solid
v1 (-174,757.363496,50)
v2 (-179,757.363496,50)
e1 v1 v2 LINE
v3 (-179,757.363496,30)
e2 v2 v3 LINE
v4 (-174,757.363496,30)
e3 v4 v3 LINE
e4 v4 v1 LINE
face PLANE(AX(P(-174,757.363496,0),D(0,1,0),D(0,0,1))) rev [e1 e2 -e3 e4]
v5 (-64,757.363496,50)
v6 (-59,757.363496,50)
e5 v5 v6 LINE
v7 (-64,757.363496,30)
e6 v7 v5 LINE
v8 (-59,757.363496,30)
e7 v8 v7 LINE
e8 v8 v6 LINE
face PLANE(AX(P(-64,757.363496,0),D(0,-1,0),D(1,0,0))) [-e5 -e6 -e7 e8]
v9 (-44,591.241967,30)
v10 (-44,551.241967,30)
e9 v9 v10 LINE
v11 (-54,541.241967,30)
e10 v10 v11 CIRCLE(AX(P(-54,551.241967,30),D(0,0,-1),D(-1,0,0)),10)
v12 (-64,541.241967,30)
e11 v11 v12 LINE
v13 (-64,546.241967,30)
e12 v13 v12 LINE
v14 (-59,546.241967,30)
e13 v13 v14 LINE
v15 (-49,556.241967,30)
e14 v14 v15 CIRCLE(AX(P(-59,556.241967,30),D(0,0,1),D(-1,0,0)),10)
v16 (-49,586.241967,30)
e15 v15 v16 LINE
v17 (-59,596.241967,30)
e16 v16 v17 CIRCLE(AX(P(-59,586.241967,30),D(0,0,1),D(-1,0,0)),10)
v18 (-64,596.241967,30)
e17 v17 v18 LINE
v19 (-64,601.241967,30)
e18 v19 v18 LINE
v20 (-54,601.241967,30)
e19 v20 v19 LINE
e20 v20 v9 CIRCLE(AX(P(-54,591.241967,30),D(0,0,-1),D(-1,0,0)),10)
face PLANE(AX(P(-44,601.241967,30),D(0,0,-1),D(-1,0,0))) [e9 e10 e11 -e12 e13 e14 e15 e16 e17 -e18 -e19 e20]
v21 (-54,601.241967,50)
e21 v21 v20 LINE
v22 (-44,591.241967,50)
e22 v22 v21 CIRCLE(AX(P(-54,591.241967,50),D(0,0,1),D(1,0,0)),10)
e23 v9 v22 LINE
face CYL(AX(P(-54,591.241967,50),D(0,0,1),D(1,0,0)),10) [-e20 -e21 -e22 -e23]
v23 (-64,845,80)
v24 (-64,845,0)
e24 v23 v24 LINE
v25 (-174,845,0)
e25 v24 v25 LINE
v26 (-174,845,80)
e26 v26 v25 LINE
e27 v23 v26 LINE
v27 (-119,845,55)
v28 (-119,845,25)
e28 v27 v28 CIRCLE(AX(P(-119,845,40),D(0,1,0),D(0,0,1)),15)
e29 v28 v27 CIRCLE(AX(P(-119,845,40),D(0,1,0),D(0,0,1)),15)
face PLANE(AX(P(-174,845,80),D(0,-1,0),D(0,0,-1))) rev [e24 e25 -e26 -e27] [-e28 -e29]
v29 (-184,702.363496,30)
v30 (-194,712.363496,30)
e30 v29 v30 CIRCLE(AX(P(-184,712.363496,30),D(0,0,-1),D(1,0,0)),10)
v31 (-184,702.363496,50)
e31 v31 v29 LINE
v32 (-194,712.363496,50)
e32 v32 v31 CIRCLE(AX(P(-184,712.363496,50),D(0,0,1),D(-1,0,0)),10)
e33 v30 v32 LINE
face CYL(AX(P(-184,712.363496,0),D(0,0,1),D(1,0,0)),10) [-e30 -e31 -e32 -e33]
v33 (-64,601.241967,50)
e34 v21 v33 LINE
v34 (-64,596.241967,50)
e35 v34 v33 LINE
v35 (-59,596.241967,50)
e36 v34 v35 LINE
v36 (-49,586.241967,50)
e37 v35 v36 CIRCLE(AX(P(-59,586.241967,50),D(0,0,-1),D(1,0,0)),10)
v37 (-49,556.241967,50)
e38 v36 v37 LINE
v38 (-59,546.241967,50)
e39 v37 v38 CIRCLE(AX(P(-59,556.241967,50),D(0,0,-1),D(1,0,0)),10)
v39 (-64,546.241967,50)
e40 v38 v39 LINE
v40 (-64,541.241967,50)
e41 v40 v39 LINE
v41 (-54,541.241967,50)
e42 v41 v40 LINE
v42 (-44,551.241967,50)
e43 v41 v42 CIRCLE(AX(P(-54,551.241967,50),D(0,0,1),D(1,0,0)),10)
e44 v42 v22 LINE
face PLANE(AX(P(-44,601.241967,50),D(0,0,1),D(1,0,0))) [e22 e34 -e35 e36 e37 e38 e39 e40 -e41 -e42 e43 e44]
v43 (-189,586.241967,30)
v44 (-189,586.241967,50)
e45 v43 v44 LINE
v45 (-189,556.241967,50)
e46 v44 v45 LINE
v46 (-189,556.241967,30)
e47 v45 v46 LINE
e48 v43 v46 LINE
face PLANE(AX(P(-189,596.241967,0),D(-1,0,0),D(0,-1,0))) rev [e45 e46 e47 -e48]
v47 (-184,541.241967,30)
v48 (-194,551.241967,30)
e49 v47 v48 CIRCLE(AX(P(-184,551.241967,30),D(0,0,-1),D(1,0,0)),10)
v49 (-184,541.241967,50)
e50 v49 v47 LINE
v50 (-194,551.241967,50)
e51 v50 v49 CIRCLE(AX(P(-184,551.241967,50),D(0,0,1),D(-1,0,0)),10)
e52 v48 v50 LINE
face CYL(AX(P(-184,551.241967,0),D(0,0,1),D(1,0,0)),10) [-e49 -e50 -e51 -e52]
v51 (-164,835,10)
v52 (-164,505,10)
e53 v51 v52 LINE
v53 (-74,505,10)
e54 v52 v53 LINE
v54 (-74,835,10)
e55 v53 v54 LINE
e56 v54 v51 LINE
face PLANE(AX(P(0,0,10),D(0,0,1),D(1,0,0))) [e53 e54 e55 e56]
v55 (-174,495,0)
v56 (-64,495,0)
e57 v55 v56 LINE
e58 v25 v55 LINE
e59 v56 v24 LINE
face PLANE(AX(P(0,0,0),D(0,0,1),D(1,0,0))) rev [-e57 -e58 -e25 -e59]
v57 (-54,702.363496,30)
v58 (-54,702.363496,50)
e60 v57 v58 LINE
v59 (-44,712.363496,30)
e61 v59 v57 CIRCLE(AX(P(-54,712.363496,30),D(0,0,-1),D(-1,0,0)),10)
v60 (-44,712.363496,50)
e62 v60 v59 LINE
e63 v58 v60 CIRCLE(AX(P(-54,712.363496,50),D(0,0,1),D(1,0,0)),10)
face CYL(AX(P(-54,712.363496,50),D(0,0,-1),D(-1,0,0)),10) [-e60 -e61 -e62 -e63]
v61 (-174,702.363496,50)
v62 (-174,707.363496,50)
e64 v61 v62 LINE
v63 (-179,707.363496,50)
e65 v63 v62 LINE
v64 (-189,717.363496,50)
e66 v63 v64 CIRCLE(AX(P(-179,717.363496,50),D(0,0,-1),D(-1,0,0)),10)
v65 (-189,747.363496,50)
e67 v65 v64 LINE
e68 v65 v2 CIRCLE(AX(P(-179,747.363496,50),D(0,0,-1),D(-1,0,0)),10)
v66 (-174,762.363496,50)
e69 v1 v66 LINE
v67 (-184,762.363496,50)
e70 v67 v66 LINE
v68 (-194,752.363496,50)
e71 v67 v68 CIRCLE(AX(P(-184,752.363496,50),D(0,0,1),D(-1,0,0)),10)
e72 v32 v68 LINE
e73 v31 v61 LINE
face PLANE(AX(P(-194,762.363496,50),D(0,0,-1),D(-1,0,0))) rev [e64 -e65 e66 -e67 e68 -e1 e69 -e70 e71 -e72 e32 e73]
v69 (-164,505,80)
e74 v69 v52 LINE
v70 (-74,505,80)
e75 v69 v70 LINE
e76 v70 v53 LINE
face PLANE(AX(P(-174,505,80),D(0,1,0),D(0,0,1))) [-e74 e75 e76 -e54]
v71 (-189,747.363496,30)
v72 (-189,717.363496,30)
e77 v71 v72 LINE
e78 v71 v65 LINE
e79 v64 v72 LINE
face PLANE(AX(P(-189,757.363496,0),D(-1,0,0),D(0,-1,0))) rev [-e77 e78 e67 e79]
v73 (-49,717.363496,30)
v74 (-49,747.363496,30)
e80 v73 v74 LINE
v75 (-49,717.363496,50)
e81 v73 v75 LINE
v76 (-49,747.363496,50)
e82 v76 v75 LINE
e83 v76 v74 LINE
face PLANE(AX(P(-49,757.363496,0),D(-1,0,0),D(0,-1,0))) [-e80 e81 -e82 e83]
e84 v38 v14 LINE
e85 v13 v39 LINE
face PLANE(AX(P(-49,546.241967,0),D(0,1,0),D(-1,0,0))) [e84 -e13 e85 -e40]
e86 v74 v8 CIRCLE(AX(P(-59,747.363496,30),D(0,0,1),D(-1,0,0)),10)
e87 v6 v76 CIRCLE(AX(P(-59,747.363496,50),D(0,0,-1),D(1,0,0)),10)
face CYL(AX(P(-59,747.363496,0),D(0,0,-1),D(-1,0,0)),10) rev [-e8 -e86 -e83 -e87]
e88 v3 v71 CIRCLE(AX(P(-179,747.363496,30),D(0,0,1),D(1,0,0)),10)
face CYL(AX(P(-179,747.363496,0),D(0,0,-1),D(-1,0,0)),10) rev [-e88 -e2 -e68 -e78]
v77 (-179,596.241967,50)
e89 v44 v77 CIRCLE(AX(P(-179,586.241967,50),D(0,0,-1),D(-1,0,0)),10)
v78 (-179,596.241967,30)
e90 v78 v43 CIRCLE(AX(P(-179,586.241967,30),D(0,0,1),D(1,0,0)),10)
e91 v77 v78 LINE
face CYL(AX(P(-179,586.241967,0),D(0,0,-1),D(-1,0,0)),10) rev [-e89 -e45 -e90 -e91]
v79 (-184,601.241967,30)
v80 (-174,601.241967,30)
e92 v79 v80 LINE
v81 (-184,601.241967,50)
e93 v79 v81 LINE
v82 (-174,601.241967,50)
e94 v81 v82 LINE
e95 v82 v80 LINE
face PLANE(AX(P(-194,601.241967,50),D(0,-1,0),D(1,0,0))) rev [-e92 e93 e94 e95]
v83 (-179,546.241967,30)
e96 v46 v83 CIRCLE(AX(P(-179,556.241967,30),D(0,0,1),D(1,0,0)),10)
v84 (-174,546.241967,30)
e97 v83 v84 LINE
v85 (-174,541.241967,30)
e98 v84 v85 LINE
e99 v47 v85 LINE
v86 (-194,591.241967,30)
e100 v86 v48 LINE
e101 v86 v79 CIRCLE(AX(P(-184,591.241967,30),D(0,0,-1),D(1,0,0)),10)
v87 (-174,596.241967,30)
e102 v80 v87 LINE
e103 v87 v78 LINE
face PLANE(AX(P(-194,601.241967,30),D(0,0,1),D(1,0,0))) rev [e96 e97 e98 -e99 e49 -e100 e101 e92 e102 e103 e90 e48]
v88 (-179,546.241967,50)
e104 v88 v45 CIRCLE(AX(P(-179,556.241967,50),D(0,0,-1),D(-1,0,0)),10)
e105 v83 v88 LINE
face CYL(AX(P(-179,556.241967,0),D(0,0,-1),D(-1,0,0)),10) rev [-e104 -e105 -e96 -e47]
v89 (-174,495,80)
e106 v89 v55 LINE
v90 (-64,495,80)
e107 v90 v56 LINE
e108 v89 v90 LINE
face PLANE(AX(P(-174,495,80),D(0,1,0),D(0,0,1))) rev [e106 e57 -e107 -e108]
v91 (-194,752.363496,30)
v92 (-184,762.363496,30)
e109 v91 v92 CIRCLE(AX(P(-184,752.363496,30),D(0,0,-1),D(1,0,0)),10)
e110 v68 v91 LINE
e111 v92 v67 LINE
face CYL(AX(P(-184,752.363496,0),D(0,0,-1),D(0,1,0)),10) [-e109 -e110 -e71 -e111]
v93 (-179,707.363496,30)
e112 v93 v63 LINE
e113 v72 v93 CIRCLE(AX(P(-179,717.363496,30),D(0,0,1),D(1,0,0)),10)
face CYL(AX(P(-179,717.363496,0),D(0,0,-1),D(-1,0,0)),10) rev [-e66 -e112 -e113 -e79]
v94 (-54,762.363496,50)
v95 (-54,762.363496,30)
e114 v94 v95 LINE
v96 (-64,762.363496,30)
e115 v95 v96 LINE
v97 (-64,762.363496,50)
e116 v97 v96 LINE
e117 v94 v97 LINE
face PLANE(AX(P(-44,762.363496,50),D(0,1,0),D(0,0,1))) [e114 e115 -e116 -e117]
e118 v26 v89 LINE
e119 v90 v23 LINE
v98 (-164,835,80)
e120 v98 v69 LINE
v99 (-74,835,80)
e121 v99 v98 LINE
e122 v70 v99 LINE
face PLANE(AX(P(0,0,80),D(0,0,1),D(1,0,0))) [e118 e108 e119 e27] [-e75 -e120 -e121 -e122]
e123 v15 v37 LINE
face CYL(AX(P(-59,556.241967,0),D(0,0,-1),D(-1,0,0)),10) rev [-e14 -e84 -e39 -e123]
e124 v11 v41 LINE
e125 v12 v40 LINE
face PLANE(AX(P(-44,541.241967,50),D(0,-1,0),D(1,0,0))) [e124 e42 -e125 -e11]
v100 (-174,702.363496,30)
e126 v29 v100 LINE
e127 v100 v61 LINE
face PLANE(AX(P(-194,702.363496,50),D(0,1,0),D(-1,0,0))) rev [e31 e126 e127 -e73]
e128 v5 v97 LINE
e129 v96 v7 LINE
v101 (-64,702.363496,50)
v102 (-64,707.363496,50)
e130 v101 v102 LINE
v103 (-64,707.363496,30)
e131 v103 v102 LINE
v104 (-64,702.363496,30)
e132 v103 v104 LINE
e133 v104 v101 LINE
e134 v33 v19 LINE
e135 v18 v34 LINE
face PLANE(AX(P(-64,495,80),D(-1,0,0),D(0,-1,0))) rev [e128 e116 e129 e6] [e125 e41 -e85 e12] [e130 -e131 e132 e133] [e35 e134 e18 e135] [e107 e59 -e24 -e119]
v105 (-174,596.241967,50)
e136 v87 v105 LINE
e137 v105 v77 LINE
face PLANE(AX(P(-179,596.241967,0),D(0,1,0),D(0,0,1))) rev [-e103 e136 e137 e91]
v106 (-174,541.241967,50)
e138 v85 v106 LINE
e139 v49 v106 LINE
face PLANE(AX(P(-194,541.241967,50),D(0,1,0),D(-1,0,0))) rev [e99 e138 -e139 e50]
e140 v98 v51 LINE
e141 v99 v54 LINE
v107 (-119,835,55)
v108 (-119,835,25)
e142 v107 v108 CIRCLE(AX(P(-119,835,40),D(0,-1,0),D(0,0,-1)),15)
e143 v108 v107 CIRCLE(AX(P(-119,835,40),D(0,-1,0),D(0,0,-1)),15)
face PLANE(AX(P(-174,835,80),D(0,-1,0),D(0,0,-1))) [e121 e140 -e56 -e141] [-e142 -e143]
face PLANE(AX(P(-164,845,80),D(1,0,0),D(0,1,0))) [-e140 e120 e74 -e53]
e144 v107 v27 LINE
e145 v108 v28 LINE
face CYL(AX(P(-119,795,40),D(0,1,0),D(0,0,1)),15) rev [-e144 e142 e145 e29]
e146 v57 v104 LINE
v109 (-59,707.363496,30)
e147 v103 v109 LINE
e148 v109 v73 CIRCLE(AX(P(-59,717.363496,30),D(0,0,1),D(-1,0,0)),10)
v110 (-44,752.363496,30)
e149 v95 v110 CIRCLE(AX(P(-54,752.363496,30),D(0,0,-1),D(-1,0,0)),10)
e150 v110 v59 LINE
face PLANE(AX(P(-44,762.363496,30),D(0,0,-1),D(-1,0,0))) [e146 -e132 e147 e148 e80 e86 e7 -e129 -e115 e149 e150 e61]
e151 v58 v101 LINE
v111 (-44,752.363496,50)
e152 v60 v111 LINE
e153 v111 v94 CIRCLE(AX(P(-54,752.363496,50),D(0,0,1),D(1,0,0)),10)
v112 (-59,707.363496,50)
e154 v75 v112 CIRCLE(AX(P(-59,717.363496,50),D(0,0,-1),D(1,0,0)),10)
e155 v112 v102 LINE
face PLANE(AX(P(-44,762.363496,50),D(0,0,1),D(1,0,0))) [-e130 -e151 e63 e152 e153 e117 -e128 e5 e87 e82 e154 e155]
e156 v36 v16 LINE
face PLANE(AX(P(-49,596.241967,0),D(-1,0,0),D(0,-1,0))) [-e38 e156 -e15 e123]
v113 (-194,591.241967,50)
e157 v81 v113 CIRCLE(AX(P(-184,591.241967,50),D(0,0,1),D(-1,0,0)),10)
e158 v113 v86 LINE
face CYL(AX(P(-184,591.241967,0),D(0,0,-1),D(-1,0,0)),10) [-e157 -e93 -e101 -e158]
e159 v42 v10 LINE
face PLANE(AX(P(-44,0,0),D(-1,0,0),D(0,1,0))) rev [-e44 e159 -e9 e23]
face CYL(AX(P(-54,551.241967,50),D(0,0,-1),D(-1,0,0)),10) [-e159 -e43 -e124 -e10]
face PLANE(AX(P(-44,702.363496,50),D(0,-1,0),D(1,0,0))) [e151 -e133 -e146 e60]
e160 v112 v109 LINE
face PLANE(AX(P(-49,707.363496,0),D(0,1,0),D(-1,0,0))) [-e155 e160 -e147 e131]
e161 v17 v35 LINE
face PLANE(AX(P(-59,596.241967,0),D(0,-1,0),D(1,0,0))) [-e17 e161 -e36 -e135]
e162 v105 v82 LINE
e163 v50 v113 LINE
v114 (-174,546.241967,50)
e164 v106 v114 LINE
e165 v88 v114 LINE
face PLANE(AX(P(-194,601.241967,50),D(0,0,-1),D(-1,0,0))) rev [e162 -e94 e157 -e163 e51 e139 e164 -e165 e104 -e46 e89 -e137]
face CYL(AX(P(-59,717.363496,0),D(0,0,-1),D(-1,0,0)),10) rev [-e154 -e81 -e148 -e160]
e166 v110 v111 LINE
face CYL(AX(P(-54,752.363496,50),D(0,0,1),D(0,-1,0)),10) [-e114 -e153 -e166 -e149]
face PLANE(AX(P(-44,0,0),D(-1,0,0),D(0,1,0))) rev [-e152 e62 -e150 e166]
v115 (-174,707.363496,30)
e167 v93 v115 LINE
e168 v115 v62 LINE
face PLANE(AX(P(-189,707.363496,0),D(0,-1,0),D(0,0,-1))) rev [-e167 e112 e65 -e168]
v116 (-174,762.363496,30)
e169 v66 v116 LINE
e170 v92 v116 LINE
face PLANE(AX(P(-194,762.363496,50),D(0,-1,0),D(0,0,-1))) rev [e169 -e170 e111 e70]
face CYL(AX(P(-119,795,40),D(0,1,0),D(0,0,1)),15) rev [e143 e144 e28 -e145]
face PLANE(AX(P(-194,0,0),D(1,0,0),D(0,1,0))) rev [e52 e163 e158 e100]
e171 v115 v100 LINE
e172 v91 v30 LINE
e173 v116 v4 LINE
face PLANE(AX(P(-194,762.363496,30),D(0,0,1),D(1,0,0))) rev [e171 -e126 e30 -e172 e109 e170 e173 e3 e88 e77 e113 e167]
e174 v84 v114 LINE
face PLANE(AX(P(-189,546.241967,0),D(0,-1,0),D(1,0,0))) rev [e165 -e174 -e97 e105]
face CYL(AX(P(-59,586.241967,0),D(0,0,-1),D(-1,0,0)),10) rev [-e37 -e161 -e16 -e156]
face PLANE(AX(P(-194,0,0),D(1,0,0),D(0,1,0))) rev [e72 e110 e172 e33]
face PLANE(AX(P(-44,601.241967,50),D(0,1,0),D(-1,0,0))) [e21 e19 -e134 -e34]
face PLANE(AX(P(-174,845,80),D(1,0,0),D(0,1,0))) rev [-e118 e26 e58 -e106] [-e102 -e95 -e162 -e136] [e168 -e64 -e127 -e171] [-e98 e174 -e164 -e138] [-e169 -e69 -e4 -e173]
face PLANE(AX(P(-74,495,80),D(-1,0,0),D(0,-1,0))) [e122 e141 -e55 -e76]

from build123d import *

# Parameters (mm, degrees)
SKETCH1_W            = 110
SKETCH1_H            = 350
BOSS_EXTRUDE1_DEPTH  = 80
SHELL1_T             = -10
SKETCH2_W            = 20
SKETCH2_H            = 60
BOSS_EXTRUDE2_DEPTH  = 20
SKETCH3_W            = 15
SKETCH3_H            = 50
CUT_EXTRUDE1_DEPTH   = 50
FILLET1_R            = 10
FILLET1_OF_MIRROR1_R = 10
SKETCH4_R            = 15
CUT_EXTRUDE2_DEPTH   = 50


with BuildPart() as part:
    # Sketch1 → Boss-Extrude1 (new body)
    with BuildSketch(Plane.XY):
        with Locations((-119, 670)):
            Rectangle(SKETCH1_W, SKETCH1_H)
    extrude(amount=BOSS_EXTRUDE1_DEPTH)

    # Shell1
    shell1_openings = [part.faces().sort_by_distance(p)[0] for p in [
        (-119, 670, 80),
    ]]
    offset(amount=SHELL1_T, openings=shell1_openings, kind=Kind.INTERSECTION)

    # Sketch2 → Boss-Extrude2 (add)
    with BuildSketch(Plane.ZY.offset(174)):
        with Locations((40, 732.363495956)):
            Rectangle(SKETCH2_W, SKETCH2_H)
        with Locations((40, 571.241967209)):
            Rectangle(SKETCH2_W, SKETCH2_H)
    boss_extrude2 = extrude(amount=BOSS_EXTRUDE2_DEPTH)

    # Sketch3 → Cut-Extrude1 (cut)
    with BuildSketch(Plane.XY.offset(50)):
        Polygon((-179, 596.241967209), (-174, 596.241967209), (-174, 546.241967209), (-179, 546.241967209), (-189, 546.241967209), (-189, 596.241967209), align=None)
        with Locations((-181.5, 732.363495956)):
            Rectangle(SKETCH3_W, SKETCH3_H)
    cut_extrude1 = extrude(amount=-CUT_EXTRUDE1_DEPTH, mode=Mode.SUBTRACT)

    # Fillet1
    fillet1_edges = [part.edges().sort_by_distance(p)[0] for p in [
        (-194, 702.363495956, 40),
        (-194, 762.363495956, 40),
        (-194, 541.241967209, 40),
        (-194, 601.241967209, 40),
        (-189, 546.241967209, 40),
        (-189, 596.241967209, 40),
        (-189, 707.363495956, 40),
        (-189, 757.363495956, 40),
    ]]
    fillet(fillet1_edges, radius=FILLET1_R)

    # Mirror1: Boss-Extrude2, Cut-Extrude1 across plane
    add(boss_extrude2.mirror(Plane(origin=(-119, 0, 0), x_dir=(0, 0, 1), z_dir=(1, 0, 0))))
    add(cut_extrude1.mirror(Plane(origin=(-119, 0, 0), x_dir=(0, 0, 1), z_dir=(1, 0, 0))), mode=Mode.SUBTRACT)

    # Fillet1 of Mirror1
    fillet1_of_mirror1_edges = [part.edges().sort_by_distance(p)[0] for p in [
        (-44, 702.363495956, 40),
        (-44, 762.363495956, 40),
        (-44, 541.241967209, 40),
        (-44, 601.241967209, 40),
        (-49, 546.241967209, 40),
        (-49, 596.241967209, 40),
        (-49, 707.363495956, 40),
        (-49, 757.363495956, 40),
    ]]
    fillet(fillet1_of_mirror1_edges, radius=FILLET1_OF_MIRROR1_R)

    # Sketch4 → Cut-Extrude2 (cut)
    with BuildSketch(Plane(origin=(0, 845, 0), x_dir=(1, 0, 0), z_dir=(0, 1, 0))):
        with Locations(Location((-119, -40, 0), (0, 0, 270))):
            Circle(SKETCH4_R)
    extrude(amount=-CUT_EXTRUDE2_DEPTH, mode=Mode.SUBTRACT)


solid = part.part
